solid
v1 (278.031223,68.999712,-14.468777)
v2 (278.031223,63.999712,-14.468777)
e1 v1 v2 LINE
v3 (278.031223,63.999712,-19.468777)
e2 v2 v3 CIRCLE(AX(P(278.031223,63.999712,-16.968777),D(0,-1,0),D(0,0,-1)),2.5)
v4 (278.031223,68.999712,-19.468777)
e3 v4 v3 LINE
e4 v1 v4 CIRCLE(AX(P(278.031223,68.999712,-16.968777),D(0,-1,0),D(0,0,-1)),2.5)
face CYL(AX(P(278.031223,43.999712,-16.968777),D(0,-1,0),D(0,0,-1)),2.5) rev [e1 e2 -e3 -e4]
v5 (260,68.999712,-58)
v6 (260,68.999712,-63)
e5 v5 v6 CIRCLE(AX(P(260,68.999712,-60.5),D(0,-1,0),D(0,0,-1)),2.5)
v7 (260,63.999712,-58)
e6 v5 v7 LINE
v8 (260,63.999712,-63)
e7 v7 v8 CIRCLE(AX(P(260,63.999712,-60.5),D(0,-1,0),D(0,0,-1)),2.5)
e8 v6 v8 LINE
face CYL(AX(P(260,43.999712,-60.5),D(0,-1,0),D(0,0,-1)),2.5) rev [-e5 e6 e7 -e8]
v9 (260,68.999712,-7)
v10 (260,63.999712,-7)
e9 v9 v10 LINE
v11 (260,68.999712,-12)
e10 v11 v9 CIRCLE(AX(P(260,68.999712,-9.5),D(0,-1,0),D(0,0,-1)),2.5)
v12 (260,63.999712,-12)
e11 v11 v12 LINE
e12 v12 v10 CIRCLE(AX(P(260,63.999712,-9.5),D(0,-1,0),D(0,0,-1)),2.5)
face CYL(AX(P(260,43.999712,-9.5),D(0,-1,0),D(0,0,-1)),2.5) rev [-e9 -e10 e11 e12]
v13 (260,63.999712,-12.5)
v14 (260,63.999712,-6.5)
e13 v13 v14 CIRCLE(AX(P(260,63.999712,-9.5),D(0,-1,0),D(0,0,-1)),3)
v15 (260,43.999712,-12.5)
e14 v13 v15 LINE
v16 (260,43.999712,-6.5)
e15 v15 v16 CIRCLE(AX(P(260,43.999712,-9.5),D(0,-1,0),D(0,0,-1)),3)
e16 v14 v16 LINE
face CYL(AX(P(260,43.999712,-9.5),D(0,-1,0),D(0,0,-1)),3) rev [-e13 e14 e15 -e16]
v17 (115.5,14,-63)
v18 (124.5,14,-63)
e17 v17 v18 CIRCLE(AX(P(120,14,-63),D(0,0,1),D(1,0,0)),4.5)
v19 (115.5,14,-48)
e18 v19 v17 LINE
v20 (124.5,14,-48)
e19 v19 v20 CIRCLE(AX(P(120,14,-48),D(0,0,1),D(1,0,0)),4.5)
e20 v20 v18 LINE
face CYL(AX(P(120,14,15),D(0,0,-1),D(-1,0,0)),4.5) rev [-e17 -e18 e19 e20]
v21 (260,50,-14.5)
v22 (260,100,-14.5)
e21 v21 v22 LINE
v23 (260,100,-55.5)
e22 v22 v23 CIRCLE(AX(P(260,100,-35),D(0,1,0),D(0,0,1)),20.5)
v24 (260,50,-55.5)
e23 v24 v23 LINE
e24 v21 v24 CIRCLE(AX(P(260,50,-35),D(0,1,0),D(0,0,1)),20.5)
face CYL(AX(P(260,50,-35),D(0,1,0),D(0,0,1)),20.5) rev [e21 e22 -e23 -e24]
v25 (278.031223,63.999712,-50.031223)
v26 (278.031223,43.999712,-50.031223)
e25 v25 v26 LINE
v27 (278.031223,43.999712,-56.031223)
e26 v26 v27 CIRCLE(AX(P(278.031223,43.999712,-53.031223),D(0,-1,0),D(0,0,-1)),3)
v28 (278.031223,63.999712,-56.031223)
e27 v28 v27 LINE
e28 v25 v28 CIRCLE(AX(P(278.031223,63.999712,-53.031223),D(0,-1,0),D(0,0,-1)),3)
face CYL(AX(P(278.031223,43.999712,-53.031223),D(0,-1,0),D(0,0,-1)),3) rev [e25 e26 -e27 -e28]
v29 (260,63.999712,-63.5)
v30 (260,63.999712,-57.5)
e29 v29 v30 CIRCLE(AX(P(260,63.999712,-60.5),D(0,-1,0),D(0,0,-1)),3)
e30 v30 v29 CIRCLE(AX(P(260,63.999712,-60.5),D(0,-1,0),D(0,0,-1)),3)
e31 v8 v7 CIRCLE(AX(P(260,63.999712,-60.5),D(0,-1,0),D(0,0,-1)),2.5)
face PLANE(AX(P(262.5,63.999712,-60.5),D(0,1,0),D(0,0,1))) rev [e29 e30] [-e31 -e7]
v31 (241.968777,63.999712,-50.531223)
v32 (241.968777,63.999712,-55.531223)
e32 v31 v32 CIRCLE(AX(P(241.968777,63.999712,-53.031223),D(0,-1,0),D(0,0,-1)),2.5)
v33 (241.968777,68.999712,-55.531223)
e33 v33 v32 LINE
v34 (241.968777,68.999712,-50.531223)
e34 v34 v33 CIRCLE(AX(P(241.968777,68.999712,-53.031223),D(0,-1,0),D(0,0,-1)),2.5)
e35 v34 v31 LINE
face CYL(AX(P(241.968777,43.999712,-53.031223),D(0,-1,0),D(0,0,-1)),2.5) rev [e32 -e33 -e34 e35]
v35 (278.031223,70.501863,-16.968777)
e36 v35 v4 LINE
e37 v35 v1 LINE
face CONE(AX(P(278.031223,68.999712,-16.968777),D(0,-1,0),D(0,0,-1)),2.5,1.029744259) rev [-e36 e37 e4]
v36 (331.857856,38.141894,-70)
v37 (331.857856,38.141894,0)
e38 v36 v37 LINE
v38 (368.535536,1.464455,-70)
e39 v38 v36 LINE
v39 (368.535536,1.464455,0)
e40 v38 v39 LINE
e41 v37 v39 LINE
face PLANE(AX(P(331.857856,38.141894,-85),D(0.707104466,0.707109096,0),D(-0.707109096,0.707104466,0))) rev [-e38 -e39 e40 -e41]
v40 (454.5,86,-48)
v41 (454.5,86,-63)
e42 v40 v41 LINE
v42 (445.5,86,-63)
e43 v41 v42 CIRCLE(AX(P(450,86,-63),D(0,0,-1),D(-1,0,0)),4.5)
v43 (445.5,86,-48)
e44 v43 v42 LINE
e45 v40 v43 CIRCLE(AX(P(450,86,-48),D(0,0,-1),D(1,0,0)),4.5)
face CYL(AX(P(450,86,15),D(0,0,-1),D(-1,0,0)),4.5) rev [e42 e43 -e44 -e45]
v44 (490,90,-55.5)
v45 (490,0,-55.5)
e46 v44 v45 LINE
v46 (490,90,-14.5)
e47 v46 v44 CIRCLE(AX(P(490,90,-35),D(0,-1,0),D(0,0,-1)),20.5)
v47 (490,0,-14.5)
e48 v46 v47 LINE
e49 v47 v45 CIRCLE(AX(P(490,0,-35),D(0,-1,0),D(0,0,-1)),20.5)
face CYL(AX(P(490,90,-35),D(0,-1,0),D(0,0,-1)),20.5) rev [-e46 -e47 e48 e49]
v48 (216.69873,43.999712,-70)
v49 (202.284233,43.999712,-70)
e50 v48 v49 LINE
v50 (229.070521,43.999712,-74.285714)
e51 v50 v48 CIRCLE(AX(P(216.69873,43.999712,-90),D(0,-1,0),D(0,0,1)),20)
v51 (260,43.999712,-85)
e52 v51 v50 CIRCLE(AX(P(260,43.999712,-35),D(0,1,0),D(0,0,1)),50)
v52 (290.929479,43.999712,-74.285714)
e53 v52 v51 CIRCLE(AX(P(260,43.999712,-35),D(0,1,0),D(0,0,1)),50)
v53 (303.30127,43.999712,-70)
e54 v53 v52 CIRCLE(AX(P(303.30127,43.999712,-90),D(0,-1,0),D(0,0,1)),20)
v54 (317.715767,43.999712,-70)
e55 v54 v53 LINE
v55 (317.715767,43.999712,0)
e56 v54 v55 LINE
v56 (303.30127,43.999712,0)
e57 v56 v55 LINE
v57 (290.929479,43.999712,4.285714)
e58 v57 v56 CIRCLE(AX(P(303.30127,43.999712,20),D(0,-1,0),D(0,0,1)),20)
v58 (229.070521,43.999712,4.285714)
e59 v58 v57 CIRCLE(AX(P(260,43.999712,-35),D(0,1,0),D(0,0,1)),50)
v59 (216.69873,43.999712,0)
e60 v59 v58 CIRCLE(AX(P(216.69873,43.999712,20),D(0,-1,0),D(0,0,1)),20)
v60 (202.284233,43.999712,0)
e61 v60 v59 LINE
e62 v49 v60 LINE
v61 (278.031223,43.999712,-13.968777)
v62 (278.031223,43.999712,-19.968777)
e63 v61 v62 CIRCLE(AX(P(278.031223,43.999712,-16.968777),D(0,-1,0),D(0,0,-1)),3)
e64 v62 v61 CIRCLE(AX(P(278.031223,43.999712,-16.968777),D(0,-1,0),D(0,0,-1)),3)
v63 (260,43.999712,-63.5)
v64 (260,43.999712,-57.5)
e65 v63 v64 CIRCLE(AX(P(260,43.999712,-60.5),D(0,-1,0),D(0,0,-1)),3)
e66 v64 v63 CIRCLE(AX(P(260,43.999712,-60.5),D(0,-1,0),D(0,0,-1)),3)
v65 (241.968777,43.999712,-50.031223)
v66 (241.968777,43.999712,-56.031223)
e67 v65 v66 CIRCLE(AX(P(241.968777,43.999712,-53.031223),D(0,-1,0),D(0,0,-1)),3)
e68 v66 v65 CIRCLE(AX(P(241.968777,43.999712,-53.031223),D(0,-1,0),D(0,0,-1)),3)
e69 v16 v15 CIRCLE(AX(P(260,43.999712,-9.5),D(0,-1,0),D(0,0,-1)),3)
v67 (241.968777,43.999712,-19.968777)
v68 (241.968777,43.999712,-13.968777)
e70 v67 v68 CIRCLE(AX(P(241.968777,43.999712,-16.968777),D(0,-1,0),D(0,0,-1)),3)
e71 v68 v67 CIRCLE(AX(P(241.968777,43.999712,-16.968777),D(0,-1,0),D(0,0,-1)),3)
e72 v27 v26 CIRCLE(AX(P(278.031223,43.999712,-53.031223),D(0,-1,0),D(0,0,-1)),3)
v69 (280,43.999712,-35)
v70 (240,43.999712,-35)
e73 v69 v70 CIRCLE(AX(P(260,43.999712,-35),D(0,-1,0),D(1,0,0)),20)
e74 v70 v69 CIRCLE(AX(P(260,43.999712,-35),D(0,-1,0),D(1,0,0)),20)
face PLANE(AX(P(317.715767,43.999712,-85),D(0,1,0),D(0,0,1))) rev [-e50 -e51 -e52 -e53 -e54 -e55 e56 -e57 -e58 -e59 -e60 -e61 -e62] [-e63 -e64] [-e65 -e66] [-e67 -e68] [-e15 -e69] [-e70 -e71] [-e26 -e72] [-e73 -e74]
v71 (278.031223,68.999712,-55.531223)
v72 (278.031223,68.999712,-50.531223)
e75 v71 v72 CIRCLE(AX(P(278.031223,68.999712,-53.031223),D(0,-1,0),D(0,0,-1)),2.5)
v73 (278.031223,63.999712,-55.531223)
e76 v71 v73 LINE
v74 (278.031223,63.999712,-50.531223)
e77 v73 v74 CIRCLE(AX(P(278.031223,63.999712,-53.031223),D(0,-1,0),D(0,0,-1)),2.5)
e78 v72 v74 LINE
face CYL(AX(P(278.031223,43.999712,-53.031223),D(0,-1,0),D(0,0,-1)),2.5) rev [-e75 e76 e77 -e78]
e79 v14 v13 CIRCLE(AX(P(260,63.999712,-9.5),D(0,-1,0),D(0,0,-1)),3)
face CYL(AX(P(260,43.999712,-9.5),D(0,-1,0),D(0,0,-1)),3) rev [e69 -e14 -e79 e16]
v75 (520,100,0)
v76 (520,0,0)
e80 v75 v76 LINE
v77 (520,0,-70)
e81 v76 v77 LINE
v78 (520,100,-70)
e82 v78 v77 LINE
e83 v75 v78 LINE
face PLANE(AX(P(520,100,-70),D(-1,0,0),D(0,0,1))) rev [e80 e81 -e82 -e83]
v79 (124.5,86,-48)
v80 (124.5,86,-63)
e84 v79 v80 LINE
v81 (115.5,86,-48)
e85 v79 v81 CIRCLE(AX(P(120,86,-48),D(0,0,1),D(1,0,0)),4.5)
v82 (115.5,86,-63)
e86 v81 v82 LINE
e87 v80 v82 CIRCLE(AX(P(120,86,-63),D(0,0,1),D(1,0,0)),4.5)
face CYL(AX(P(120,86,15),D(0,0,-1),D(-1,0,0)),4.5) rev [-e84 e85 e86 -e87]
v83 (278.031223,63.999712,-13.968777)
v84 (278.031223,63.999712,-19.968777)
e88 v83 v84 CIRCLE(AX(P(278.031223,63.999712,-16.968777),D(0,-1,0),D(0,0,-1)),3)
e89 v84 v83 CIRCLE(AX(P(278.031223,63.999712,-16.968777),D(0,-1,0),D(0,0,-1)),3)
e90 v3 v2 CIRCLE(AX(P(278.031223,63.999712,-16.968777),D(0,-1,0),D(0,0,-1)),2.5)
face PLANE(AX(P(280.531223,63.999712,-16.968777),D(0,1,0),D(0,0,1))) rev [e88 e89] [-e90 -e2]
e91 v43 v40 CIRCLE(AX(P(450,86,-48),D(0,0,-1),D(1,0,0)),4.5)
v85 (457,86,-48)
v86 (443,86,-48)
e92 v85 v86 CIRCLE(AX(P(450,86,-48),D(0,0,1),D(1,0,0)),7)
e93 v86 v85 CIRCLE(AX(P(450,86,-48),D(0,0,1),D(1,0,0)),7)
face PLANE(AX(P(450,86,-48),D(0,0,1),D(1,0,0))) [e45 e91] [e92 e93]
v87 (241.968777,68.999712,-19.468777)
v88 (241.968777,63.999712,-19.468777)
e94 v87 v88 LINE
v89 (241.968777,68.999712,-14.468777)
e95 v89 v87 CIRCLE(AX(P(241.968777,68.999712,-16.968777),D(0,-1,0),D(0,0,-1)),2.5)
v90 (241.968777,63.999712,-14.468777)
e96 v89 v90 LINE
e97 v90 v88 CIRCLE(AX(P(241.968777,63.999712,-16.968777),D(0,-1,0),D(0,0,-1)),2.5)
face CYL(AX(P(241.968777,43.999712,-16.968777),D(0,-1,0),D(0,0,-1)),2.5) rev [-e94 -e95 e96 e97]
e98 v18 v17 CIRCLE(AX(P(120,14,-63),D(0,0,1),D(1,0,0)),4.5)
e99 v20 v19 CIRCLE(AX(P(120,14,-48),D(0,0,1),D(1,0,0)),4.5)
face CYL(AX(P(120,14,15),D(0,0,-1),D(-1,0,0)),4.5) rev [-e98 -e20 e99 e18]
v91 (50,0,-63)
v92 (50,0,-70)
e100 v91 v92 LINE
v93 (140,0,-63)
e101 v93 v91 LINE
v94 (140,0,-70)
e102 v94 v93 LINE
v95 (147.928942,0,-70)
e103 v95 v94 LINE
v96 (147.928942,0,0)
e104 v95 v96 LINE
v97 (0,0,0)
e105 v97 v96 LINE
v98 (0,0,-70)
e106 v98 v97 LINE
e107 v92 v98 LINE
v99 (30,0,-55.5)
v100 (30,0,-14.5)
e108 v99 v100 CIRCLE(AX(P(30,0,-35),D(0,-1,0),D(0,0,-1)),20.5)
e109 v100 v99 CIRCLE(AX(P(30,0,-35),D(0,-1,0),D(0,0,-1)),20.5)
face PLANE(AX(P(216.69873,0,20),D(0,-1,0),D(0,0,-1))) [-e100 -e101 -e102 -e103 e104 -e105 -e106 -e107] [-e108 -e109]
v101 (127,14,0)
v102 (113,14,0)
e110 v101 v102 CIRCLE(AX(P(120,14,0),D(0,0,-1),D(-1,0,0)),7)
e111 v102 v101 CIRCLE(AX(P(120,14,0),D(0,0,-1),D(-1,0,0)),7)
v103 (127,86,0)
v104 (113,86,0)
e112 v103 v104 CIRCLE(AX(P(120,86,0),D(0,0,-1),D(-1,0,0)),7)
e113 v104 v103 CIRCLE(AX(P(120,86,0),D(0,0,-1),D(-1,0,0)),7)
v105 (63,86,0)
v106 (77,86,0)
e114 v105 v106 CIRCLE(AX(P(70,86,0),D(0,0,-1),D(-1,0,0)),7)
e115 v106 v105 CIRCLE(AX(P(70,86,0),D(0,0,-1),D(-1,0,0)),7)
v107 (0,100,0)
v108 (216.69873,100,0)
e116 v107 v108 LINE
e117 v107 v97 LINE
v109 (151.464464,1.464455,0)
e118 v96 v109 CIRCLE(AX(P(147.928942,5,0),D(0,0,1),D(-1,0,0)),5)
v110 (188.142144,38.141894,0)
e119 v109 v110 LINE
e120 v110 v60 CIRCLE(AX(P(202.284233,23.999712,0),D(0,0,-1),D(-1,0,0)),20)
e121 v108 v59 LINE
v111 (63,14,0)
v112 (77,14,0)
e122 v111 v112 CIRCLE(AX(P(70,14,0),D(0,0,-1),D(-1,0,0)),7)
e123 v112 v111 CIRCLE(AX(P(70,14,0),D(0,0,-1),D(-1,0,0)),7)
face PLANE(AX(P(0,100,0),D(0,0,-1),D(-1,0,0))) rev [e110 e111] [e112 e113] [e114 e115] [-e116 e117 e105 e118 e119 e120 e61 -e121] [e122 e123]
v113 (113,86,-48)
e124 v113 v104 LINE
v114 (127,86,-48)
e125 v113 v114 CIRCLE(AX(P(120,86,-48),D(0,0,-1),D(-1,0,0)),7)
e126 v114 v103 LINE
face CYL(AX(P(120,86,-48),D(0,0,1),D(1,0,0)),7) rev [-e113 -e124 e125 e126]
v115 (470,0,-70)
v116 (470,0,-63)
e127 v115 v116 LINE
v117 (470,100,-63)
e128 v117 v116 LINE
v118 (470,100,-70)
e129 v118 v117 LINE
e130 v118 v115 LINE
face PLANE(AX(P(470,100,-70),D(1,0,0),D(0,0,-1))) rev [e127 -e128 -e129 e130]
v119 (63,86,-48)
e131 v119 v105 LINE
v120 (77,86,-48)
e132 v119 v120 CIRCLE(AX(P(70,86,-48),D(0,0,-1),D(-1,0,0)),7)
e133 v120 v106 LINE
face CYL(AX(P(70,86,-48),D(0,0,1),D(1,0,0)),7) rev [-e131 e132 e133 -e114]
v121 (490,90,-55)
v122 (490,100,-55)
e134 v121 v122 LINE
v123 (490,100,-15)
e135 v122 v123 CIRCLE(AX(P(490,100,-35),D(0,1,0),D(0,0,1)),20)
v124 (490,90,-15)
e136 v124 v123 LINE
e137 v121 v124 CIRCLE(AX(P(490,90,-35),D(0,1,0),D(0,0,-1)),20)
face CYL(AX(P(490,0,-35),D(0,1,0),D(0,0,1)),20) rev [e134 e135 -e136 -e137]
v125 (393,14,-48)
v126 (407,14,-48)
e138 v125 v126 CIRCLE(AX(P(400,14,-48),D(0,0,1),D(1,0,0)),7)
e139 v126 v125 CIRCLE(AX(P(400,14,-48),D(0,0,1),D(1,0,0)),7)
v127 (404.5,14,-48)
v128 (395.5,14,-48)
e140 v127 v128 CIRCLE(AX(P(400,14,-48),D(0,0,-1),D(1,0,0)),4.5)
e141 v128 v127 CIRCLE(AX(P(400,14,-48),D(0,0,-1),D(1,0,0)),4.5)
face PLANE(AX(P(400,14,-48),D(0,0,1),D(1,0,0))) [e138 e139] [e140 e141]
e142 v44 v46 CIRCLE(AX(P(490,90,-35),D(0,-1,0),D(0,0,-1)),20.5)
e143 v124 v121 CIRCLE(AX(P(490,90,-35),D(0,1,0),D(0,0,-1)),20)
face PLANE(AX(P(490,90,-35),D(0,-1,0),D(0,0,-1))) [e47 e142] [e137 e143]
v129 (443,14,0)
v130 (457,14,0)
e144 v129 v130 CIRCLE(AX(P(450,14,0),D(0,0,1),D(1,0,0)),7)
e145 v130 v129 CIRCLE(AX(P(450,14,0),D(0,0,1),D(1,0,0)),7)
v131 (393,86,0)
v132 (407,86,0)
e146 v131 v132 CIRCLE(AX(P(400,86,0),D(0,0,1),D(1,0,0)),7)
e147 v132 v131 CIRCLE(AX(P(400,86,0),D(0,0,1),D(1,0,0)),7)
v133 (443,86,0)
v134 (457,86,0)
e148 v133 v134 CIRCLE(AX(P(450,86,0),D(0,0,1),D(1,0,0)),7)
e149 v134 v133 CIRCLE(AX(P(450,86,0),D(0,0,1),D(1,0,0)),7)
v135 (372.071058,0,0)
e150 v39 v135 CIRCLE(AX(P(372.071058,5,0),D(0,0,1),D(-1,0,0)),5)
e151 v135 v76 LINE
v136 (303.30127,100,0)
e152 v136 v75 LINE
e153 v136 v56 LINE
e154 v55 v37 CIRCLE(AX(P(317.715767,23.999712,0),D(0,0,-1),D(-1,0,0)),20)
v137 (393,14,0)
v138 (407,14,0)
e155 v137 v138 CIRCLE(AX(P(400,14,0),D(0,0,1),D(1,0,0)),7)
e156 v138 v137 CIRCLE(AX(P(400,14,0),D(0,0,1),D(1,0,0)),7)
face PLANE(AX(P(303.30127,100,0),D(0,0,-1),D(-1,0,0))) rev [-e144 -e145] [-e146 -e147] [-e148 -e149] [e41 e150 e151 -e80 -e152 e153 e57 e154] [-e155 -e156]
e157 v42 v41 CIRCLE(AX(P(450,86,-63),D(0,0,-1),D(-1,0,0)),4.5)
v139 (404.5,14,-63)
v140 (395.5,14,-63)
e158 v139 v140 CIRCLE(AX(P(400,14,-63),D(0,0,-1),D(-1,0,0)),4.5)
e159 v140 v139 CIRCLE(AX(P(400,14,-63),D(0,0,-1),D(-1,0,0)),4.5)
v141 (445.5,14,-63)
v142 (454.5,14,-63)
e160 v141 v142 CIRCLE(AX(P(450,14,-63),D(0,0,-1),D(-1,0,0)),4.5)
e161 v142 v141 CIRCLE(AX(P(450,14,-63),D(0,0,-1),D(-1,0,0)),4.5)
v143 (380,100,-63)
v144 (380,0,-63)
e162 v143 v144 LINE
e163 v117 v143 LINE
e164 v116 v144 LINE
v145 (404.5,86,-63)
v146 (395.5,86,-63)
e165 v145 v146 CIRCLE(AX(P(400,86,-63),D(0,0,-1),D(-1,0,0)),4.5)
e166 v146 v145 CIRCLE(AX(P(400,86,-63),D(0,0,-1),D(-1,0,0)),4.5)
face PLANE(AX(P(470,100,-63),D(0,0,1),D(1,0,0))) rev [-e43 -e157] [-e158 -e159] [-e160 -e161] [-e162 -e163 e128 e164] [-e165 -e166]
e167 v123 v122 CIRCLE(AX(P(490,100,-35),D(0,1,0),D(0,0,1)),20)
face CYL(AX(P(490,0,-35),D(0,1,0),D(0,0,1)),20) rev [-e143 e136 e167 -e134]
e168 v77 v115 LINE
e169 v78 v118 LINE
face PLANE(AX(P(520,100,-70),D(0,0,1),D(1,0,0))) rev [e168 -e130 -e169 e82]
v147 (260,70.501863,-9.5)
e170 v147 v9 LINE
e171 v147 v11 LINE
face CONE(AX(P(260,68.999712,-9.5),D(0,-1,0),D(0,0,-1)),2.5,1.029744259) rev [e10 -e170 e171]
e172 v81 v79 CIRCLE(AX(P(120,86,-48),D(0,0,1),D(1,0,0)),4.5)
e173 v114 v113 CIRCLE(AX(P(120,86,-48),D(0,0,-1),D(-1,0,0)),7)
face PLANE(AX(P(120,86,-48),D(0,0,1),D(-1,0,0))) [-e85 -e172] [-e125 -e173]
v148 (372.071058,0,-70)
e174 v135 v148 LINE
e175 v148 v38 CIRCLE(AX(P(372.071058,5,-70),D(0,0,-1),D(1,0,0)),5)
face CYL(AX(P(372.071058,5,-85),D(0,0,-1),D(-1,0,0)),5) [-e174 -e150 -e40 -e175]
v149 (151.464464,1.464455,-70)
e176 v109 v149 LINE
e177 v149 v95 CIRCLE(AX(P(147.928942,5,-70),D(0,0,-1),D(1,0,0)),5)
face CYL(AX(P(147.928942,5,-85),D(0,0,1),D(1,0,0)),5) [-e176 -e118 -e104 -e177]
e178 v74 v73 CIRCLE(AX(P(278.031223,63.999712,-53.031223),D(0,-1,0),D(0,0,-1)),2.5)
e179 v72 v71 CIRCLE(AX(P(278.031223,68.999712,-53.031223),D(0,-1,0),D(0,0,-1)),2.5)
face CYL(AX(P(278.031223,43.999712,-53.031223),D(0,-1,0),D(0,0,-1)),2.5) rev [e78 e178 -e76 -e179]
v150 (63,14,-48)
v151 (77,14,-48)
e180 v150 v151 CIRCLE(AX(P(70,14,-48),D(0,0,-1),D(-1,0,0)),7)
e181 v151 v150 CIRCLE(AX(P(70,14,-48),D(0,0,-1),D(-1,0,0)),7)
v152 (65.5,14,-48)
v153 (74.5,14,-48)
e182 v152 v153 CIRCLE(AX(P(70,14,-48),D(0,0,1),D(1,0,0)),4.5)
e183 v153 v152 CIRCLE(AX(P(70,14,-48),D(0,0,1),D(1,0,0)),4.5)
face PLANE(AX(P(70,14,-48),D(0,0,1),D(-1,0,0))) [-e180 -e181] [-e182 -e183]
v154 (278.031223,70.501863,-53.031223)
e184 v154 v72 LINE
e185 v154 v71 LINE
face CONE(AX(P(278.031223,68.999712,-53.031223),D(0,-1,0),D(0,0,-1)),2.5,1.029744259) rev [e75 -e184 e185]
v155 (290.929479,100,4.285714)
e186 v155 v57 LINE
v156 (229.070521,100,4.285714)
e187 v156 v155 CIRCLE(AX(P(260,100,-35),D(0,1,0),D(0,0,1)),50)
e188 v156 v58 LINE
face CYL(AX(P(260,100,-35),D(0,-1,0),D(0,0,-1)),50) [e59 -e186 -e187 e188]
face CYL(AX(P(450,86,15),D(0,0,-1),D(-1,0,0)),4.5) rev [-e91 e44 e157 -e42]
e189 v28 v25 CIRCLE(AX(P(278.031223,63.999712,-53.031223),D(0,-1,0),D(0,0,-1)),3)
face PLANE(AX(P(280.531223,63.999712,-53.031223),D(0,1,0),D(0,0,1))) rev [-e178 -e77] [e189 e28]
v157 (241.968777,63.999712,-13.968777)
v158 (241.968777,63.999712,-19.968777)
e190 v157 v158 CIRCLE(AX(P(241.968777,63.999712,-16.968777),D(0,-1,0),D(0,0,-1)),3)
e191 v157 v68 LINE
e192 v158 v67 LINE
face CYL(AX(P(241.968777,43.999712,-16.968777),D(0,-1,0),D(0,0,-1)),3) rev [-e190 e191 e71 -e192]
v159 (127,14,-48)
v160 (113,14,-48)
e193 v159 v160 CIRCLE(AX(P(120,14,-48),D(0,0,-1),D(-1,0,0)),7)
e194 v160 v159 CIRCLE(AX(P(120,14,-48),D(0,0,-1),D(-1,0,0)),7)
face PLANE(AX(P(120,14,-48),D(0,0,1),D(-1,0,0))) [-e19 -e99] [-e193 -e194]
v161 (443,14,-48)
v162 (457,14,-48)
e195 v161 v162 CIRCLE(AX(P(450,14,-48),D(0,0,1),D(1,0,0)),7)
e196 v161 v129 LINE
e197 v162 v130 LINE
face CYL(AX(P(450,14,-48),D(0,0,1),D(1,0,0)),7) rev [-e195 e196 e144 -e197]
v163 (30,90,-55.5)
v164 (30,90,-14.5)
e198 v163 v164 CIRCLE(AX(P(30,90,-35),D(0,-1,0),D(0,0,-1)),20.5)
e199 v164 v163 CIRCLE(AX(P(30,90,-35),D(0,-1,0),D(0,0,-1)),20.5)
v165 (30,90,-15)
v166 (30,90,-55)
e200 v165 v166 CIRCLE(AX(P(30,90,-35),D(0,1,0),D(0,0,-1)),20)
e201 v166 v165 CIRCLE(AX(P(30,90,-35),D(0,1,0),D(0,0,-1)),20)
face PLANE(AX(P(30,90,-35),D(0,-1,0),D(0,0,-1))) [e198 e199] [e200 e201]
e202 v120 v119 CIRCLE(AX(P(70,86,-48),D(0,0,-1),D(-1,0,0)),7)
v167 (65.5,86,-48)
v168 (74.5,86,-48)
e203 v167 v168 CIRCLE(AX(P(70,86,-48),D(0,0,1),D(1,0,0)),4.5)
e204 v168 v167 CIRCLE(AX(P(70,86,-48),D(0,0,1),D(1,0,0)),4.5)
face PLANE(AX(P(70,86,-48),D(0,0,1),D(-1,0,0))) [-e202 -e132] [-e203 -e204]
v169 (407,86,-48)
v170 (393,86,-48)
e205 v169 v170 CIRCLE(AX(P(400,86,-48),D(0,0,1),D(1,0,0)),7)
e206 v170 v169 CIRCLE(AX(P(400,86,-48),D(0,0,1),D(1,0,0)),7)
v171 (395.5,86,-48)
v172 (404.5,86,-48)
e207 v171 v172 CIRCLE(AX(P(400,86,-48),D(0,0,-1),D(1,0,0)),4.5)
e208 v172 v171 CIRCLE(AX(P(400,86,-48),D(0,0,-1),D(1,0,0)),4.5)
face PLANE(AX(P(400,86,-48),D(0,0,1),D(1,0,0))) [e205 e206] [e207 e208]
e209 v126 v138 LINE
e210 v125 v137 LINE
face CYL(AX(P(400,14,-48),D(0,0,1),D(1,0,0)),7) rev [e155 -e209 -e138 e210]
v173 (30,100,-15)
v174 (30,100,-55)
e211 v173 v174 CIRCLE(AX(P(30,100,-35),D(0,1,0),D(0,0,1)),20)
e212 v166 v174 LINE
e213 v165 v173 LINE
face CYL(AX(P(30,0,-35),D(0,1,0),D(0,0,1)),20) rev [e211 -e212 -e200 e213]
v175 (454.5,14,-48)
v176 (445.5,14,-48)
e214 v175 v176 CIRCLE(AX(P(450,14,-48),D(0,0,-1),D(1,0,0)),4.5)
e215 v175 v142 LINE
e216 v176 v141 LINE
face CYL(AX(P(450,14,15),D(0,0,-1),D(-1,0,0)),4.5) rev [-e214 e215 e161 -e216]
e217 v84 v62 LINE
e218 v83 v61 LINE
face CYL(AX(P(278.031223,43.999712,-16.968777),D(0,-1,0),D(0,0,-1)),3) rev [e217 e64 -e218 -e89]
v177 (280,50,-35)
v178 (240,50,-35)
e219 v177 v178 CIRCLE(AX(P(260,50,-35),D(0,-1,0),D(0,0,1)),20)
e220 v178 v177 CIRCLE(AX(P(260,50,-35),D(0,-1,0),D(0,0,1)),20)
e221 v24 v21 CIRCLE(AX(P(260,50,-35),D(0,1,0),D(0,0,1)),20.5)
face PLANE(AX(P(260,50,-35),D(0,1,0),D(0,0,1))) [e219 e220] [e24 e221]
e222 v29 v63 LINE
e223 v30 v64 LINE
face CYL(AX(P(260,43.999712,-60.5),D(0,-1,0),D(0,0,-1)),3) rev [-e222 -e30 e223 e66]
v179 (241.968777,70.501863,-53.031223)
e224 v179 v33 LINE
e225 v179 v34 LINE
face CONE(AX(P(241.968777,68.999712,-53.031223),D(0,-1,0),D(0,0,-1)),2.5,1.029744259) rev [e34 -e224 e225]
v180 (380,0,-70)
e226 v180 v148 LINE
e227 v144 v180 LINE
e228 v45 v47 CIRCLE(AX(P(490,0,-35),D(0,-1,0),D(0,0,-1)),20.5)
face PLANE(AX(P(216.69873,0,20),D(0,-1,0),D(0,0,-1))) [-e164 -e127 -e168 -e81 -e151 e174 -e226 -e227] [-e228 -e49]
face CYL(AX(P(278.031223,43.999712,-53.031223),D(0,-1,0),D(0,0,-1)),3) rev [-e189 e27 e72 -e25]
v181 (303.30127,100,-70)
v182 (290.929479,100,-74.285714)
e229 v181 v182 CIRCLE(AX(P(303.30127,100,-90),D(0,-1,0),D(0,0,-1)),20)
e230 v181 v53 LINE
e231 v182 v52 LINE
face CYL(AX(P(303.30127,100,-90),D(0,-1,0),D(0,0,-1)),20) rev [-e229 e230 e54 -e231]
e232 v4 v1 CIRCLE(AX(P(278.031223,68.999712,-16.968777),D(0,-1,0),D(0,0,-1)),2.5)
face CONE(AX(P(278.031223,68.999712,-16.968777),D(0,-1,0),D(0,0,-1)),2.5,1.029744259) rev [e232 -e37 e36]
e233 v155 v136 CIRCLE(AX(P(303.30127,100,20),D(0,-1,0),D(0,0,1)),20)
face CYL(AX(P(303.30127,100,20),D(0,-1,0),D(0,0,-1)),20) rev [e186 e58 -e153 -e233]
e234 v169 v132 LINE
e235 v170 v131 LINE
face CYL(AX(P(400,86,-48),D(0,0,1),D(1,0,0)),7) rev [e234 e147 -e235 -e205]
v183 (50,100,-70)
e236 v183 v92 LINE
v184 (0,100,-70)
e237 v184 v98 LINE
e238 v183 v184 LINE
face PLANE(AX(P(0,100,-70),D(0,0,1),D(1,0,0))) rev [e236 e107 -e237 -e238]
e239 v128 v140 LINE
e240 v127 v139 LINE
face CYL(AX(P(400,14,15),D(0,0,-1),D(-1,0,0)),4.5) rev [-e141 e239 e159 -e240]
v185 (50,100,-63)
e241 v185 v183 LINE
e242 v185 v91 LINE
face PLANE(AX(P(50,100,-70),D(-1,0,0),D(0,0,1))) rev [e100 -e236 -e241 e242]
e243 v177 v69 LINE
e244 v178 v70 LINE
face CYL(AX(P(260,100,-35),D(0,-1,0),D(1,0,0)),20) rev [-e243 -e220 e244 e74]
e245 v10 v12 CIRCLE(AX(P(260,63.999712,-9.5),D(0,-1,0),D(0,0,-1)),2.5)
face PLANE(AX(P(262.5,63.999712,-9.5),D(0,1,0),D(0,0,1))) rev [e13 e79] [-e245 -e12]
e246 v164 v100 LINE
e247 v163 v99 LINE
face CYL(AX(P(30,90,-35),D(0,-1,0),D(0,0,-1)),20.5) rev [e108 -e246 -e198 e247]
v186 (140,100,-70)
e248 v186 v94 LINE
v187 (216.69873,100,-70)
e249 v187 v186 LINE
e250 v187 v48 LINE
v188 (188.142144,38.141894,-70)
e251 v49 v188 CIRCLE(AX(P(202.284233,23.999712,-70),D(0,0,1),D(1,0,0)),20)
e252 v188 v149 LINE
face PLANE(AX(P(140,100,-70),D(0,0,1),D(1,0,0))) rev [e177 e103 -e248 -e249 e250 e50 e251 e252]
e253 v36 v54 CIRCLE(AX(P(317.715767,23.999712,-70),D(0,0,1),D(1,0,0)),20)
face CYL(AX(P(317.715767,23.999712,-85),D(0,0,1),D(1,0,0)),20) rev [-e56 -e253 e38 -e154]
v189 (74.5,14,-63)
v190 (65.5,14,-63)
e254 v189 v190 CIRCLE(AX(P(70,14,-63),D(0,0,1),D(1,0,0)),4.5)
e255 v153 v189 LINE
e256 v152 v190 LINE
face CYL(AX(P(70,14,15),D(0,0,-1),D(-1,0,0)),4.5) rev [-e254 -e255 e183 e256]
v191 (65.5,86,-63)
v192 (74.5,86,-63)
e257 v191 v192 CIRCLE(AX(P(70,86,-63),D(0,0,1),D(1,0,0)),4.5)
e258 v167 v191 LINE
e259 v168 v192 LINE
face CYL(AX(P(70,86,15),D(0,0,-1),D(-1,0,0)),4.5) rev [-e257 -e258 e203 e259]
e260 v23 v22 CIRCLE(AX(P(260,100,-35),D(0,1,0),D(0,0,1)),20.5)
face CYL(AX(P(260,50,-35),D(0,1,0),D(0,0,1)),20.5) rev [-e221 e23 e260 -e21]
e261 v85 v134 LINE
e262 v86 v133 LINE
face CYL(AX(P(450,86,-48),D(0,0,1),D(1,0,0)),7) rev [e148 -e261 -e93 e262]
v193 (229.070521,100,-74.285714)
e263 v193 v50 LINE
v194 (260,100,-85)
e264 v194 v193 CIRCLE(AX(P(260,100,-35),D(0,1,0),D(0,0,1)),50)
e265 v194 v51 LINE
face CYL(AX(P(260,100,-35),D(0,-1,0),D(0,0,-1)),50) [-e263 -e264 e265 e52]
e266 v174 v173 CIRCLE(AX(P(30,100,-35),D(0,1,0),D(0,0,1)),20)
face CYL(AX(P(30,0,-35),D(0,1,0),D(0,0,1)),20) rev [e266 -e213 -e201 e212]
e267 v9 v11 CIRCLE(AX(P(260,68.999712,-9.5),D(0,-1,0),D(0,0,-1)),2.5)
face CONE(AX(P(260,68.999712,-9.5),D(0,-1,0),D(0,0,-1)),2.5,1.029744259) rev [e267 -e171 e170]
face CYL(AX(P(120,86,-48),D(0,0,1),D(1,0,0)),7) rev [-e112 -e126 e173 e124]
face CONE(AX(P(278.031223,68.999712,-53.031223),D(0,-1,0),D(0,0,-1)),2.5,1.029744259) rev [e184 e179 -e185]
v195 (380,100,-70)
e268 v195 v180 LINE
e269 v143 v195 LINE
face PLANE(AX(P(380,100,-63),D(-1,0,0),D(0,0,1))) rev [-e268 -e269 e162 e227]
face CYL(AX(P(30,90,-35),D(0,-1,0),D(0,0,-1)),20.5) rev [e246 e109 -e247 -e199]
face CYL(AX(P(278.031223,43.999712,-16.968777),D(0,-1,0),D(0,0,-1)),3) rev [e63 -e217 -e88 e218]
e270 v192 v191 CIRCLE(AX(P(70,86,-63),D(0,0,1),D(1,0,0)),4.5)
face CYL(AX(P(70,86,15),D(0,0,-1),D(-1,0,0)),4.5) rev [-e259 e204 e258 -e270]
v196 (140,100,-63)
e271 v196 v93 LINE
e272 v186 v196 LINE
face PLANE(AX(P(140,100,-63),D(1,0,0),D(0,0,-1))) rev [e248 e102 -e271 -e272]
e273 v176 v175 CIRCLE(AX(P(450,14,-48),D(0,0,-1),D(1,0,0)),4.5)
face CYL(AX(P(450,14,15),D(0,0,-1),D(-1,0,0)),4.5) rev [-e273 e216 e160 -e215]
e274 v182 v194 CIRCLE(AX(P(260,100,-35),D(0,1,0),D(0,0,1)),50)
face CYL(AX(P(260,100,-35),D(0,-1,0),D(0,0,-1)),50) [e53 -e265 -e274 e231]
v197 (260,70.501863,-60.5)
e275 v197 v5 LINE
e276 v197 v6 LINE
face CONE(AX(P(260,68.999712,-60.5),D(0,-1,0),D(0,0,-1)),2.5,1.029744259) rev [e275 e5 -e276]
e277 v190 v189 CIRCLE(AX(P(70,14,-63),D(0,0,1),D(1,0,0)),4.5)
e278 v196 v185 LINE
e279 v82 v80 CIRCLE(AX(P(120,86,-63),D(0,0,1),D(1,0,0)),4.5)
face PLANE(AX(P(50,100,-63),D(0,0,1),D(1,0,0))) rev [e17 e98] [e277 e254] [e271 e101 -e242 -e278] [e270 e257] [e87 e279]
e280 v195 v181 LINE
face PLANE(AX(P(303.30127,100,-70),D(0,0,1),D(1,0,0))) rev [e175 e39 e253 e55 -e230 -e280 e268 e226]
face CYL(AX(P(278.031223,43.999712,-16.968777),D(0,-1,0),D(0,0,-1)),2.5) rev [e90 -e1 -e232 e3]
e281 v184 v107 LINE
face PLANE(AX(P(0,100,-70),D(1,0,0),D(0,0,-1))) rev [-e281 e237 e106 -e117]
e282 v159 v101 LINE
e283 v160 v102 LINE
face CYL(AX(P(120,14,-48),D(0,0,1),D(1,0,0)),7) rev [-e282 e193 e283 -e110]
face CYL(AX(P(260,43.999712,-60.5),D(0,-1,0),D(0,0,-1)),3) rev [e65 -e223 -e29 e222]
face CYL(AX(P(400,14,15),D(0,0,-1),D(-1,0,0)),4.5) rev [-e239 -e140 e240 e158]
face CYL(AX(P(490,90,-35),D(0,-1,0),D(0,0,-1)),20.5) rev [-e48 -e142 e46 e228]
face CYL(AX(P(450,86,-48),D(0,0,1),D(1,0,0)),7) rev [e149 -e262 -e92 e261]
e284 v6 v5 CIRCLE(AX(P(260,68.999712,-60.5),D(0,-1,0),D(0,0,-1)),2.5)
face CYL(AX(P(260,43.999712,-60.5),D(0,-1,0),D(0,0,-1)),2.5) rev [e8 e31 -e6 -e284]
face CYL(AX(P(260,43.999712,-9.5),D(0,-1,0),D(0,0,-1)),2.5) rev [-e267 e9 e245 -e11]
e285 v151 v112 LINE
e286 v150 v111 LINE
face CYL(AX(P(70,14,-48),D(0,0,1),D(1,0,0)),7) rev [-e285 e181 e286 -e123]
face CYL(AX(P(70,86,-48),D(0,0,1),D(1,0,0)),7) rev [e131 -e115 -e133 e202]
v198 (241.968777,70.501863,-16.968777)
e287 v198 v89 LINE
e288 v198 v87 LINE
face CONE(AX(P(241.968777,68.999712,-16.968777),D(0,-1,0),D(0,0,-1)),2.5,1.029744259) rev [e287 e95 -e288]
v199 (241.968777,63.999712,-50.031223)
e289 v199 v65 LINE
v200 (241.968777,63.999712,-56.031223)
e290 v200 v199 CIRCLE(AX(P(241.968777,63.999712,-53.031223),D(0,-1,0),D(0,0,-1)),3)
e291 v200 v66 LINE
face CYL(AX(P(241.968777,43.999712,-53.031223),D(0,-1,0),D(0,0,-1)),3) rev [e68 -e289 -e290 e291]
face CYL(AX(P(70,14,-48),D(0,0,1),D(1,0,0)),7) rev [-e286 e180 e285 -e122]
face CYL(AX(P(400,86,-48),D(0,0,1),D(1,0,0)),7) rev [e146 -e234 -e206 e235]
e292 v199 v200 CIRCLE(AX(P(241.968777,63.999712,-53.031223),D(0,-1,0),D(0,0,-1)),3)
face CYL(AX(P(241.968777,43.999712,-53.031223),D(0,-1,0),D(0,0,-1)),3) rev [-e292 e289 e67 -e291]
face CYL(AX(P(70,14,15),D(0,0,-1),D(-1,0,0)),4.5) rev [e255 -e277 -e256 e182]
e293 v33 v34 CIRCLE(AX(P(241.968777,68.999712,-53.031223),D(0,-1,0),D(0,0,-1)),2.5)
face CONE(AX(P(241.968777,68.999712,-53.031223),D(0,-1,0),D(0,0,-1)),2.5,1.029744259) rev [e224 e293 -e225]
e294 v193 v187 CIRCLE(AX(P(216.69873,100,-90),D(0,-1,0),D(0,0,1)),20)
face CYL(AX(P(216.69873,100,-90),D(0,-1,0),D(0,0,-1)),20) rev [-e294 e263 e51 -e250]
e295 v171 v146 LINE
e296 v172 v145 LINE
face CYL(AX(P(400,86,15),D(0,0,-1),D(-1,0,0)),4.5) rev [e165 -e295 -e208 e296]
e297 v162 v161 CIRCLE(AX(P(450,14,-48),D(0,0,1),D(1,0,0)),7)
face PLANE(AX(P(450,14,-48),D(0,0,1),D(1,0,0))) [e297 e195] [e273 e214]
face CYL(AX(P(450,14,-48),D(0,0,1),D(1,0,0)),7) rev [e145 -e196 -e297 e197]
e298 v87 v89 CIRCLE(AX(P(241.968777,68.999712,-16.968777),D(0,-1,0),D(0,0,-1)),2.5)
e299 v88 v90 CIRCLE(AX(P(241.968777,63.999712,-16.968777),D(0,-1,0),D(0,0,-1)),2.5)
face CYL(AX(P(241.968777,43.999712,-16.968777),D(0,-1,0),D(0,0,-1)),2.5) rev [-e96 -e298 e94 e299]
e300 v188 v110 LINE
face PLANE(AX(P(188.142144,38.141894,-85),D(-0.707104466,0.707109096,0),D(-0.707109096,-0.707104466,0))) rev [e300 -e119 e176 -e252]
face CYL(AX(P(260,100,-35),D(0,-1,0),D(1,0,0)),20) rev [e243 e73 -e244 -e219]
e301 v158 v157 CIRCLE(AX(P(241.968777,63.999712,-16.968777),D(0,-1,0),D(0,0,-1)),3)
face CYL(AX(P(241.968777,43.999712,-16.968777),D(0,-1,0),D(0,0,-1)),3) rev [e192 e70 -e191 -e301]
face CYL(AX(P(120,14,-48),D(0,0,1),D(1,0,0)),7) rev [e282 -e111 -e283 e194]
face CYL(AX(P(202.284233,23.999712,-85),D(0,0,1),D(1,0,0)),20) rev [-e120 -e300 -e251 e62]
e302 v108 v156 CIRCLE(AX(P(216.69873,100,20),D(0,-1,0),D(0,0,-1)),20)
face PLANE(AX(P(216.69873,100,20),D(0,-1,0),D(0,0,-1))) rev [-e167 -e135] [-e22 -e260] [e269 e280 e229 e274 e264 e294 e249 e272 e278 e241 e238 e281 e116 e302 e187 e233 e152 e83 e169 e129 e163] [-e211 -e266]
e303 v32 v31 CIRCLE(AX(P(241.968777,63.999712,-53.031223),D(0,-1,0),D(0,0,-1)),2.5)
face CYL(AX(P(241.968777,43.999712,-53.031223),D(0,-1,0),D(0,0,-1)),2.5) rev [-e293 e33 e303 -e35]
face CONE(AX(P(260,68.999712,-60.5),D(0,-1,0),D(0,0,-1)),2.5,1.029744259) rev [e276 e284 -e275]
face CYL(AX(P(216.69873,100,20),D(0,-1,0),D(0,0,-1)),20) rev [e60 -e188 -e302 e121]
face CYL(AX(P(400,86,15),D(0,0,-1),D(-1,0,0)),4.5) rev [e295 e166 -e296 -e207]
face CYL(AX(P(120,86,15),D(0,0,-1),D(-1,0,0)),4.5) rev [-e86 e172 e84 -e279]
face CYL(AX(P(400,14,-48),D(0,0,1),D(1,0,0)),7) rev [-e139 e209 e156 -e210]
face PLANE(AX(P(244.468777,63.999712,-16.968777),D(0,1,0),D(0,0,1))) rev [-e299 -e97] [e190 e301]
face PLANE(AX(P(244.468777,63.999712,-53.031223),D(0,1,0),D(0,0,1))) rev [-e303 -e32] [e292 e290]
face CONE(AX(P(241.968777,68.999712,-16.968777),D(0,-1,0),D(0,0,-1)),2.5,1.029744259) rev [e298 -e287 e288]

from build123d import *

# Parameters (mm, degrees)
EXTRUDE_1_DEPTH              = 100
CUT_EXTRUDE_1_DEPTH          = 537.306815172
CUT_EXTRUDE_1_DEPTH_BACK     = 537.306815172
SKETCH_3_R                   = 20
CUT_EXTRUDE_2_DEPTH          = 530.868882144
SKETCH_7_R                   = 4.5
CUT_EXTRUDE_4_DEPTH          = 536.242001341
SKETCH_8_R                   = 7
CUT_EXTRUDE_5_DEPTH          = 48
SKETCH_13_R                  = 20
CUT_EXTRUDE_7_DEPTH          = 537.306815172
SKETCH_12_R                  = 1
CUT_EXTRUDE_8_DEPTH          = 10
HOLE_WIZARD_M6_1_D           = 5
HOLE_WIZARD_M6_1_DEPTH       = 25
HOLE_WIZARD_M6_1_CBORE_D     = 6
HOLE_WIZARD_M6_1_CBORE_DEPTH = 20
HOLE_WIZARD_M6_1_TIP         = 1.502151548
SKETCH_18_R                  = 20.5
CUT_EXTRUDE_9_DEPTH          = 90
SKETCH_19_R                  = 20.5
CUT_EXTRUDE_10_DEPTH         = 50
FILLET_1_R                   = 5


with BuildPart() as part:
    # 草图1 → 拉伸1 (new body)
    with BuildSketch(Plane(origin=(0, 0, 0), x_dir=(1, 0, 0), z_dir=(0, 1, 0))):
        with BuildLine():
            Line((0, 70), (0, 0))
            Line((0, 0), (216.698729811, 0))
            ThreePointArc((216.698729811, 0), (223.245266518, -1.10177635), (229.070521293, -4.285714286))
            ThreePointArc((229.070521293, -4.285714286), (260, -15), (290.929478707, -4.285714286))
            ThreePointArc((290.929478707, -4.285714286), (296.754733482, -1.10177635), (303.301270189, 0))
            Line((303.301270189, 0), (520, 0))
            Line((520, 0), (520, 70))
            Line((520, 70), (470, 70))
            Line((470, 70), (470, 63))
            Line((470, 63), (380, 63))
            Line((380, 63), (380, 70))
            Line((380, 70), (303.301270189, 70))
            ThreePointArc((303.301270189, 70), (296.754733482, 71.10177635), (290.929478707, 74.285714286))
            ThreePointArc((290.929478707, 74.285714286), (260, 85), (229.070521293, 74.285714286))
            ThreePointArc((229.070521293, 74.285714286), (223.245266518, 71.10177635), (216.698729811, 70))
            Line((216.698729811, 70), (140, 70))
            Line((140, 70), (140, 63))
            Line((140, 63), (50, 63))
            Line((50, 63), (50, 70))
            Line((50, 70), (0, 70))
        make_face()
    extrude(amount=EXTRUDE_1_DEPTH)

    # 草图2 → 切除-拉伸1 (cut, two sides: drawn at the far end of the back side and taken through both)
    with BuildSketch(Plane.XY.offset(-CUT_EXTRUDE_1_DEPTH_BACK)):
        with BuildLine():
            Line((317.715767105, 43.999711923), (202.284232895, 43.999711923))
            ThreePointArc((202.284232895, 43.999711923), (194.630594492, 42.477315101), (188.142143567, 38.141893843))
            Line((188.142143567, 38.141893843), (150, 0))
            Line((150, 0), (370, 0))
            Line((370, 0), (331.857856433, 38.141893843))
            ThreePointArc((331.857856433, 38.141893843), (325.369405508, 42.477315101), (317.715767105, 43.999711923))
        make_face()
    extrude(amount=CUT_EXTRUDE_1_DEPTH + CUT_EXTRUDE_1_DEPTH_BACK, mode=Mode.SUBTRACT)

    # 草图3 → 切除-拉伸2 (cut, through all)
    with BuildSketch(Plane.XZ.offset(-43.999711923)):
        with Locations((260, -35)):
            Circle(SKETCH_3_R)
    extrude(amount=-CUT_EXTRUDE_2_DEPTH, mode=Mode.SUBTRACT)

    # 草图7 → 切除-拉伸4 (cut, through all)
    with BuildSketch(Plane(origin=(0, 0, -63), x_dir=(-1, 0, 0), z_dir=(0, 0, -1))):
        with Locations((-450, 86)):
            Circle(SKETCH_7_R)
        with Locations((-400, 86)):
            Circle(SKETCH_7_R)
        with Locations((-400, 14)):
            Circle(SKETCH_7_R)
        with Locations((-450, 14)):
            Circle(SKETCH_7_R)
    cut_extrude_4 = extrude(amount=-CUT_EXTRUDE_4_DEPTH, mode=Mode.SUBTRACT)

    # 草图8 → 切除-拉伸5 (cut)
    with BuildSketch(Plane.XY):
        with Locations((400, 86)):
            Circle(SKETCH_8_R)
        with Locations((450, 86)):
            Circle(SKETCH_8_R)
        with Locations((450, 14)):
            Circle(SKETCH_8_R)
        with Locations((400, 14)):
            Circle(SKETCH_8_R)
    cut_extrude_5 = extrude(amount=-CUT_EXTRUDE_5_DEPTH, mode=Mode.SUBTRACT)

    # 镜向2: 切除-拉伸4, 切除-拉伸5 across plane
    add(cut_extrude_4.mirror(Plane(origin=(260, 0, 0), x_dir=(0, 0, 1), z_dir=(1, 0, 0))), mode=Mode.SUBTRACT)
    add(cut_extrude_5.mirror(Plane(origin=(260, 0, 0), x_dir=(0, 0, 1), z_dir=(1, 0, 0))), mode=Mode.SUBTRACT)

    # 草图13 → 切除-拉伸7 (cut, through all)
    with BuildSketch(Plane(origin=(0, 100, 0), x_dir=(1, 0, 0), z_dir=(0, 1, 0))):
        with Locations(Location((30, 35, 0), (0, 0, 270))):
            Circle(SKETCH_13_R)
        with Locations(Location((490, 35, 0), (0, 0, 270))):
            Circle(SKETCH_13_R)
    extrude(amount=-CUT_EXTRUDE_7_DEPTH, mode=Mode.SUBTRACT)

    # 草图12 → 切除-拉伸8 (cut)
    with BuildSketch(Plane.XZ.offset(-43.999711923)):
        with Locations(Location((260, -9.5, 0), (0, 0, 270))):
            Circle(SKETCH_12_R)
        with Locations(Location((241.96877708, -16.96877708, 0), (0, 0, 270))):
            Circle(SKETCH_12_R)
        with Locations(Location((278.03122292, -16.96877708, 0), (0, 0, 270))):
            Circle(SKETCH_12_R)
        with Locations(Location((241.96877708, -53.03122292, 0), (0, 0, 270))):
            Circle(SKETCH_12_R)
        with Locations(Location((260, -60.5, 0), (0, 0, 270))):
            Circle(SKETCH_12_R)
        with Locations(Location((278.03122292, -53.03122292, 0), (0, 0, 270))):
            Circle(SKETCH_12_R)
    extrude(amount=-CUT_EXTRUDE_8_DEPTH, mode=Mode.SUBTRACT)

    # M6 螺纹孔1
    with Locations(Plane.XZ.offset(-43.999711923)):
        with Locations((260, -9.5), (241.96877708, -16.96877708), (278.03122292, -16.96877708), (278.03122292, -53.03122292), (260, -60.5), (241.96877708, -53.03122292)):
            CounterBoreHole(HOLE_WIZARD_M6_1_D / 2, HOLE_WIZARD_M6_1_CBORE_D / 2, HOLE_WIZARD_M6_1_CBORE_DEPTH, depth=HOLE_WIZARD_M6_1_DEPTH)
            with Locations((0, 0, -(HOLE_WIZARD_M6_1_DEPTH + HOLE_WIZARD_M6_1_TIP / 2))):  # 118° drill point
                Cone(0, HOLE_WIZARD_M6_1_D / 2, HOLE_WIZARD_M6_1_TIP, mode=Mode.SUBTRACT)

    # 草图18 → 切除-拉伸9 (cut)
    with BuildSketch(Plane.XZ):
        with Locations(Location((30, -35, 0), (0, 0, 270))):
            Circle(SKETCH_18_R)
        with Locations(Location((490, -35, 0), (0, 0, 270))):
            Circle(SKETCH_18_R)
    extrude(amount=-CUT_EXTRUDE_9_DEPTH, mode=Mode.SUBTRACT)

    # 草图19 → 切除-拉伸10 (cut)
    with BuildSketch(Plane(origin=(0, 100, 0), x_dir=(1, 0, 0), z_dir=(0, 1, 0))):
        with Locations(Location((260, 35, 0), (0, 0, 270))):
            Circle(SKETCH_19_R)
    extrude(amount=-CUT_EXTRUDE_10_DEPTH, mode=Mode.SUBTRACT)

    # 圆角1
    fillet_1_edges = [part.edges().sort_by_distance(p)[0] for p in [
        (150, 0, -35),
        (370, 0, -35),
    ]]
    fillet(fillet_1_edges, radius=FILLET_1_R)


solid = part.part
